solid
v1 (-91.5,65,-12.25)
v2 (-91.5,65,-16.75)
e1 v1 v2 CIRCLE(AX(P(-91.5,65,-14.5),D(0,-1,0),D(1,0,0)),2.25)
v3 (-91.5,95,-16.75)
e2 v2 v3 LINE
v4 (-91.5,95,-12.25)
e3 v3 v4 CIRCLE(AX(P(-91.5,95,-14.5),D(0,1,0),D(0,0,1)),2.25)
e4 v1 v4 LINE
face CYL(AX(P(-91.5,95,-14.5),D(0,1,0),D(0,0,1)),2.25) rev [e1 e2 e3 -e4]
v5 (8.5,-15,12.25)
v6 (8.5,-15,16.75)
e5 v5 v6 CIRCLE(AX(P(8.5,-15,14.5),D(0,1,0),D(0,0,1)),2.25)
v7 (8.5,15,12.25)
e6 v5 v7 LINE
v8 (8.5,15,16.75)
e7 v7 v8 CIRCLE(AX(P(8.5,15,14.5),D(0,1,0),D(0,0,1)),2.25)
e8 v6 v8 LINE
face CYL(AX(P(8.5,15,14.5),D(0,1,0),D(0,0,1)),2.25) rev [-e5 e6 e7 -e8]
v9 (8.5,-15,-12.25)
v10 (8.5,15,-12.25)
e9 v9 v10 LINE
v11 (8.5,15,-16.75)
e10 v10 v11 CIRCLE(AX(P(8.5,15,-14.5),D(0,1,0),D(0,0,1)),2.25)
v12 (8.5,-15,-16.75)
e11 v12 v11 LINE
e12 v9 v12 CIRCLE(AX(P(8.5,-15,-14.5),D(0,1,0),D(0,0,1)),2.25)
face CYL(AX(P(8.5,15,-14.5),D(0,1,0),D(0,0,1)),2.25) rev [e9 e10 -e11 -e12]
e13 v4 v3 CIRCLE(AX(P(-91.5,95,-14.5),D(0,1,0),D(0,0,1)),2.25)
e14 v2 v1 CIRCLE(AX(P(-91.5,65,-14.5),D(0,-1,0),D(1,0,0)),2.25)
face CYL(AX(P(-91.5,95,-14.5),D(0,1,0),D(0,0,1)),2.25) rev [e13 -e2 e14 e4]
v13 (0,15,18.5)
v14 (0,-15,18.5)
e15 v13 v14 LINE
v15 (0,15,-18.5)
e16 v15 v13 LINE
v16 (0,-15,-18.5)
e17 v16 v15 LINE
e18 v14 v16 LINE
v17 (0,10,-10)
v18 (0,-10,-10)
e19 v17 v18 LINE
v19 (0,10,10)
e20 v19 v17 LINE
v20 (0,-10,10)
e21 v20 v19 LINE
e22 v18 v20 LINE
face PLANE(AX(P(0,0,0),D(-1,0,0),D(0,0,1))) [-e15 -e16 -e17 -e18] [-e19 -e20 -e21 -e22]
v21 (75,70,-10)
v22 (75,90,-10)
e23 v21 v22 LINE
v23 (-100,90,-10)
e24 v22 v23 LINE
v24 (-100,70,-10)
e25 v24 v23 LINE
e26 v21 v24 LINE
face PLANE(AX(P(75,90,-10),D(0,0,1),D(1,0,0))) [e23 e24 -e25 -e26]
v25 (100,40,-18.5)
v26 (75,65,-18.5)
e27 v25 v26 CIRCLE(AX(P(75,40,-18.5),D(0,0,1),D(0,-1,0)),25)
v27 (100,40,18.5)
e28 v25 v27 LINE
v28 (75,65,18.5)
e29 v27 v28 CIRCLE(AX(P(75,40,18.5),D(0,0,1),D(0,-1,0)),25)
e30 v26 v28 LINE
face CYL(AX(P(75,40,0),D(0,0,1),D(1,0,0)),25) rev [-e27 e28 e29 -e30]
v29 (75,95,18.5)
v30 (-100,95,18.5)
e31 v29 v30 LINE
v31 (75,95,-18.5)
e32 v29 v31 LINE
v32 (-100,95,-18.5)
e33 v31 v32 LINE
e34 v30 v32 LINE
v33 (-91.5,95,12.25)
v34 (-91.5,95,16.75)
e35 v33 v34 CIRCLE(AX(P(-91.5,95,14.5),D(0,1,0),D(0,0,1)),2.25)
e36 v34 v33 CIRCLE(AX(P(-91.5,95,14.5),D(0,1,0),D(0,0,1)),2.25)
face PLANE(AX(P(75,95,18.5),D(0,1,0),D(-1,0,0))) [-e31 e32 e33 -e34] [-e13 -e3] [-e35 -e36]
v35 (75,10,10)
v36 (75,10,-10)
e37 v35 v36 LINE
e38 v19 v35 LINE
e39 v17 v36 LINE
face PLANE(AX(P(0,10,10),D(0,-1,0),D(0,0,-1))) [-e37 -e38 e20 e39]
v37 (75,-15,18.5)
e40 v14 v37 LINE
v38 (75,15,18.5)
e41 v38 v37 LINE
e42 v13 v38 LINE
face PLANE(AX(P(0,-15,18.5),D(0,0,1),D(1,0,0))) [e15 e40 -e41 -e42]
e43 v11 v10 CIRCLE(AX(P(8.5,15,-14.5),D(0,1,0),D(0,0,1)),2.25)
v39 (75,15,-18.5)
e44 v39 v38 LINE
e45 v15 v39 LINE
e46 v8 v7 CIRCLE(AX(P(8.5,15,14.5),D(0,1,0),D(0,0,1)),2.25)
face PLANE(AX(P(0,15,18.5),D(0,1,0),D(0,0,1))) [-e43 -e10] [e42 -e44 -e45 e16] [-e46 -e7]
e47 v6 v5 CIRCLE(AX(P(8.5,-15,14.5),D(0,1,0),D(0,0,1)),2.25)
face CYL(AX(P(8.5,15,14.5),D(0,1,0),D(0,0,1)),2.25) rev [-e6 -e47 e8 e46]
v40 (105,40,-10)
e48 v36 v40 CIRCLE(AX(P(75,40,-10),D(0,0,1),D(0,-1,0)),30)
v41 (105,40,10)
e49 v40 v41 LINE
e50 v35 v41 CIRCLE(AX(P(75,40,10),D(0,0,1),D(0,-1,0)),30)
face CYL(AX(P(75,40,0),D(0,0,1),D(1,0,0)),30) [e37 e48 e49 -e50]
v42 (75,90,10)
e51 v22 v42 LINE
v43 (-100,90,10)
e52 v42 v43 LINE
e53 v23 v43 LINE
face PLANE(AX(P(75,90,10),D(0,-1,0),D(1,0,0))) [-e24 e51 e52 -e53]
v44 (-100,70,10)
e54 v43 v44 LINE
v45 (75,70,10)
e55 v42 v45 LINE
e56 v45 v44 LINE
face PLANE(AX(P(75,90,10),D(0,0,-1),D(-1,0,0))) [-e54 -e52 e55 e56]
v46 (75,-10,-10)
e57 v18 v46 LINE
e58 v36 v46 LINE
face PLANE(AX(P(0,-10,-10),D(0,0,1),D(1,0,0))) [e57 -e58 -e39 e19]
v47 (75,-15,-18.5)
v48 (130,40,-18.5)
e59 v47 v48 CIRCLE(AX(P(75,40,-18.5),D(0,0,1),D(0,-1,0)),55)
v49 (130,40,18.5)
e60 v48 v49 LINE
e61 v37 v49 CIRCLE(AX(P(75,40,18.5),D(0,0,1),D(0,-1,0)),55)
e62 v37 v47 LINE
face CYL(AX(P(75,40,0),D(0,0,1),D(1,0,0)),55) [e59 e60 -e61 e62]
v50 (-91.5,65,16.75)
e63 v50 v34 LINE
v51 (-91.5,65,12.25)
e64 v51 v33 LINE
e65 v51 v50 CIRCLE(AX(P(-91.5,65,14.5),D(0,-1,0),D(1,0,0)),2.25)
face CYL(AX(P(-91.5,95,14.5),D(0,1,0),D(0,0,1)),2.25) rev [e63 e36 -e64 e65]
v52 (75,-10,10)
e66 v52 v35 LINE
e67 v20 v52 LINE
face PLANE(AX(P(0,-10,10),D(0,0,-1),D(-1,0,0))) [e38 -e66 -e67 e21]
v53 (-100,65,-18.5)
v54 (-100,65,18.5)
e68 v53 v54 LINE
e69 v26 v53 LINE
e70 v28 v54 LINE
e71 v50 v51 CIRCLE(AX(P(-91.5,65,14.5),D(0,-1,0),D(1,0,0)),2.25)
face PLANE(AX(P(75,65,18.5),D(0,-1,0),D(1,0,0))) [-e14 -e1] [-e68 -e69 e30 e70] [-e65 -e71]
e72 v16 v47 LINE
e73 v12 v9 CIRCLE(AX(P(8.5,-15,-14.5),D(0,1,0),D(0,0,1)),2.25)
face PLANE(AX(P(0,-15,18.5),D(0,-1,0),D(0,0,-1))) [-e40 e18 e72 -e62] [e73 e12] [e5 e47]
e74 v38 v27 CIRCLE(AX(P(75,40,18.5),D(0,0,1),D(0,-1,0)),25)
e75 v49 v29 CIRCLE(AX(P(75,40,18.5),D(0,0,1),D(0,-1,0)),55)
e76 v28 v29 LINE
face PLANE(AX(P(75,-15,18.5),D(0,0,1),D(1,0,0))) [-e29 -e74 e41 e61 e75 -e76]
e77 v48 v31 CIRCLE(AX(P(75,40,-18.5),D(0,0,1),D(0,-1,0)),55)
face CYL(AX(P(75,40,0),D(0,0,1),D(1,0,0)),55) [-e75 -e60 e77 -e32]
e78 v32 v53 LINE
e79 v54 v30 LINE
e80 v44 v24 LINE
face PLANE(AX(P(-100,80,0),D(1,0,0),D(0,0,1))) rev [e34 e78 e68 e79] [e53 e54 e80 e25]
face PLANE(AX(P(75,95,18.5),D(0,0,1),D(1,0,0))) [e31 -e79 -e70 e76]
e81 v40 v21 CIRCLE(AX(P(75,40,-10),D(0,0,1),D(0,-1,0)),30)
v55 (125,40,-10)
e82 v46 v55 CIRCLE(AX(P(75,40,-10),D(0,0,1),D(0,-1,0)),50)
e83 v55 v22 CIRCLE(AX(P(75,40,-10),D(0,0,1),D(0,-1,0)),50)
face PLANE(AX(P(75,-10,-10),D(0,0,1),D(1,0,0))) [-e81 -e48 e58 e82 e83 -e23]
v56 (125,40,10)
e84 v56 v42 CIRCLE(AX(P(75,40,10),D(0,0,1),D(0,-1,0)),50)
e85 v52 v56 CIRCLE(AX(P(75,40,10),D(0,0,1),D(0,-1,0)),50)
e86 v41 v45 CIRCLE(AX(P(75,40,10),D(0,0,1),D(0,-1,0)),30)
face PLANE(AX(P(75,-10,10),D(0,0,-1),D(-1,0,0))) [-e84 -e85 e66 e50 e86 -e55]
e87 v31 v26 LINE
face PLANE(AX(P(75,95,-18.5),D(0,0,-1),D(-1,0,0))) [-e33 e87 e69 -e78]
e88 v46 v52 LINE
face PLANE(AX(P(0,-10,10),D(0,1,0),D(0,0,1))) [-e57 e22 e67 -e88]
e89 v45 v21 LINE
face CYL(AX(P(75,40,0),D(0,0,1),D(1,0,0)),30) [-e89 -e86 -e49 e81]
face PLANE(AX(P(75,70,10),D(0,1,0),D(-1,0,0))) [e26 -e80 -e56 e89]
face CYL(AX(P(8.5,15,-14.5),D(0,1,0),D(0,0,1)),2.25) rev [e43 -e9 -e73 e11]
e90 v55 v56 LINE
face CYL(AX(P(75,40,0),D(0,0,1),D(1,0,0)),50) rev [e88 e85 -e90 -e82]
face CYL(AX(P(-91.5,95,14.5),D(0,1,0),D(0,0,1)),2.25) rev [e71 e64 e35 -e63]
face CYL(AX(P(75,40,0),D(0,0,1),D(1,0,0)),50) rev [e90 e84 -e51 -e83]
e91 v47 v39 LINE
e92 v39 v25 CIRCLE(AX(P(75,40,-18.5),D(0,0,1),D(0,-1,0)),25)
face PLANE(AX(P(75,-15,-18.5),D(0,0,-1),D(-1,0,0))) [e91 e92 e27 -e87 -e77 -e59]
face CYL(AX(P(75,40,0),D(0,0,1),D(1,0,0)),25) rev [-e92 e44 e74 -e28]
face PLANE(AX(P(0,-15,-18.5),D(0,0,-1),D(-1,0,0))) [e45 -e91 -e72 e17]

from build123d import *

# Parameters (mm, degrees)
SKETCH1_W                = 37
SKETCH1_H                = 30
SKETCH1_W_2              = 20
SKETCH1_H_2              = 20
M4_CLEARANCE_HOLE1_D     = 4.5
M4_CLEARANCE_HOLE1_DEPTH = 30
M4_CLEARANCE_HOLE2_D     = 4.5


with BuildPart() as part:
    # Sweep1: sweep along a path in Sketch2
    with BuildLine(Plane.XY) as sweep1_path:
        Line((0, 0), (75, 0))
        ThreePointArc((75, 0), (115, 40), (75, 80))
        Line((75, 80), (-100, 80))
    # Sketch1 → Sweep1 (sweep)
    with BuildSketch(Plane(origin=(0, 0, 0), x_dir=(0, 0, -1), z_dir=(1, 0, 0))):
        Rectangle(SKETCH1_W, SKETCH1_H)
        Rectangle(SKETCH1_W_2, SKETCH1_H_2, mode=Mode.SUBTRACT)
    sweep(path=sweep1_path.line)

    # M4 Clearance Hole1
    with Locations(Plane(origin=(0, 15, 0), x_dir=(1, 0, 0), z_dir=(0, 1, 0))):
        with Locations((8.5, 14.5), (8.5, -14.5)):
            Hole(M4_CLEARANCE_HOLE1_D / 2, depth=M4_CLEARANCE_HOLE1_DEPTH)

    # M4 Clearance Hole2 (through all)
    with Locations(Plane(origin=(0, 95, 0), x_dir=(1, 0, 0), z_dir=(0, 1, 0))):
        with Locations((-91.5, -14.5), (-91.5, 14.5)):
            Hole(M4_CLEARANCE_HOLE2_D / 2)


solid = part.part
